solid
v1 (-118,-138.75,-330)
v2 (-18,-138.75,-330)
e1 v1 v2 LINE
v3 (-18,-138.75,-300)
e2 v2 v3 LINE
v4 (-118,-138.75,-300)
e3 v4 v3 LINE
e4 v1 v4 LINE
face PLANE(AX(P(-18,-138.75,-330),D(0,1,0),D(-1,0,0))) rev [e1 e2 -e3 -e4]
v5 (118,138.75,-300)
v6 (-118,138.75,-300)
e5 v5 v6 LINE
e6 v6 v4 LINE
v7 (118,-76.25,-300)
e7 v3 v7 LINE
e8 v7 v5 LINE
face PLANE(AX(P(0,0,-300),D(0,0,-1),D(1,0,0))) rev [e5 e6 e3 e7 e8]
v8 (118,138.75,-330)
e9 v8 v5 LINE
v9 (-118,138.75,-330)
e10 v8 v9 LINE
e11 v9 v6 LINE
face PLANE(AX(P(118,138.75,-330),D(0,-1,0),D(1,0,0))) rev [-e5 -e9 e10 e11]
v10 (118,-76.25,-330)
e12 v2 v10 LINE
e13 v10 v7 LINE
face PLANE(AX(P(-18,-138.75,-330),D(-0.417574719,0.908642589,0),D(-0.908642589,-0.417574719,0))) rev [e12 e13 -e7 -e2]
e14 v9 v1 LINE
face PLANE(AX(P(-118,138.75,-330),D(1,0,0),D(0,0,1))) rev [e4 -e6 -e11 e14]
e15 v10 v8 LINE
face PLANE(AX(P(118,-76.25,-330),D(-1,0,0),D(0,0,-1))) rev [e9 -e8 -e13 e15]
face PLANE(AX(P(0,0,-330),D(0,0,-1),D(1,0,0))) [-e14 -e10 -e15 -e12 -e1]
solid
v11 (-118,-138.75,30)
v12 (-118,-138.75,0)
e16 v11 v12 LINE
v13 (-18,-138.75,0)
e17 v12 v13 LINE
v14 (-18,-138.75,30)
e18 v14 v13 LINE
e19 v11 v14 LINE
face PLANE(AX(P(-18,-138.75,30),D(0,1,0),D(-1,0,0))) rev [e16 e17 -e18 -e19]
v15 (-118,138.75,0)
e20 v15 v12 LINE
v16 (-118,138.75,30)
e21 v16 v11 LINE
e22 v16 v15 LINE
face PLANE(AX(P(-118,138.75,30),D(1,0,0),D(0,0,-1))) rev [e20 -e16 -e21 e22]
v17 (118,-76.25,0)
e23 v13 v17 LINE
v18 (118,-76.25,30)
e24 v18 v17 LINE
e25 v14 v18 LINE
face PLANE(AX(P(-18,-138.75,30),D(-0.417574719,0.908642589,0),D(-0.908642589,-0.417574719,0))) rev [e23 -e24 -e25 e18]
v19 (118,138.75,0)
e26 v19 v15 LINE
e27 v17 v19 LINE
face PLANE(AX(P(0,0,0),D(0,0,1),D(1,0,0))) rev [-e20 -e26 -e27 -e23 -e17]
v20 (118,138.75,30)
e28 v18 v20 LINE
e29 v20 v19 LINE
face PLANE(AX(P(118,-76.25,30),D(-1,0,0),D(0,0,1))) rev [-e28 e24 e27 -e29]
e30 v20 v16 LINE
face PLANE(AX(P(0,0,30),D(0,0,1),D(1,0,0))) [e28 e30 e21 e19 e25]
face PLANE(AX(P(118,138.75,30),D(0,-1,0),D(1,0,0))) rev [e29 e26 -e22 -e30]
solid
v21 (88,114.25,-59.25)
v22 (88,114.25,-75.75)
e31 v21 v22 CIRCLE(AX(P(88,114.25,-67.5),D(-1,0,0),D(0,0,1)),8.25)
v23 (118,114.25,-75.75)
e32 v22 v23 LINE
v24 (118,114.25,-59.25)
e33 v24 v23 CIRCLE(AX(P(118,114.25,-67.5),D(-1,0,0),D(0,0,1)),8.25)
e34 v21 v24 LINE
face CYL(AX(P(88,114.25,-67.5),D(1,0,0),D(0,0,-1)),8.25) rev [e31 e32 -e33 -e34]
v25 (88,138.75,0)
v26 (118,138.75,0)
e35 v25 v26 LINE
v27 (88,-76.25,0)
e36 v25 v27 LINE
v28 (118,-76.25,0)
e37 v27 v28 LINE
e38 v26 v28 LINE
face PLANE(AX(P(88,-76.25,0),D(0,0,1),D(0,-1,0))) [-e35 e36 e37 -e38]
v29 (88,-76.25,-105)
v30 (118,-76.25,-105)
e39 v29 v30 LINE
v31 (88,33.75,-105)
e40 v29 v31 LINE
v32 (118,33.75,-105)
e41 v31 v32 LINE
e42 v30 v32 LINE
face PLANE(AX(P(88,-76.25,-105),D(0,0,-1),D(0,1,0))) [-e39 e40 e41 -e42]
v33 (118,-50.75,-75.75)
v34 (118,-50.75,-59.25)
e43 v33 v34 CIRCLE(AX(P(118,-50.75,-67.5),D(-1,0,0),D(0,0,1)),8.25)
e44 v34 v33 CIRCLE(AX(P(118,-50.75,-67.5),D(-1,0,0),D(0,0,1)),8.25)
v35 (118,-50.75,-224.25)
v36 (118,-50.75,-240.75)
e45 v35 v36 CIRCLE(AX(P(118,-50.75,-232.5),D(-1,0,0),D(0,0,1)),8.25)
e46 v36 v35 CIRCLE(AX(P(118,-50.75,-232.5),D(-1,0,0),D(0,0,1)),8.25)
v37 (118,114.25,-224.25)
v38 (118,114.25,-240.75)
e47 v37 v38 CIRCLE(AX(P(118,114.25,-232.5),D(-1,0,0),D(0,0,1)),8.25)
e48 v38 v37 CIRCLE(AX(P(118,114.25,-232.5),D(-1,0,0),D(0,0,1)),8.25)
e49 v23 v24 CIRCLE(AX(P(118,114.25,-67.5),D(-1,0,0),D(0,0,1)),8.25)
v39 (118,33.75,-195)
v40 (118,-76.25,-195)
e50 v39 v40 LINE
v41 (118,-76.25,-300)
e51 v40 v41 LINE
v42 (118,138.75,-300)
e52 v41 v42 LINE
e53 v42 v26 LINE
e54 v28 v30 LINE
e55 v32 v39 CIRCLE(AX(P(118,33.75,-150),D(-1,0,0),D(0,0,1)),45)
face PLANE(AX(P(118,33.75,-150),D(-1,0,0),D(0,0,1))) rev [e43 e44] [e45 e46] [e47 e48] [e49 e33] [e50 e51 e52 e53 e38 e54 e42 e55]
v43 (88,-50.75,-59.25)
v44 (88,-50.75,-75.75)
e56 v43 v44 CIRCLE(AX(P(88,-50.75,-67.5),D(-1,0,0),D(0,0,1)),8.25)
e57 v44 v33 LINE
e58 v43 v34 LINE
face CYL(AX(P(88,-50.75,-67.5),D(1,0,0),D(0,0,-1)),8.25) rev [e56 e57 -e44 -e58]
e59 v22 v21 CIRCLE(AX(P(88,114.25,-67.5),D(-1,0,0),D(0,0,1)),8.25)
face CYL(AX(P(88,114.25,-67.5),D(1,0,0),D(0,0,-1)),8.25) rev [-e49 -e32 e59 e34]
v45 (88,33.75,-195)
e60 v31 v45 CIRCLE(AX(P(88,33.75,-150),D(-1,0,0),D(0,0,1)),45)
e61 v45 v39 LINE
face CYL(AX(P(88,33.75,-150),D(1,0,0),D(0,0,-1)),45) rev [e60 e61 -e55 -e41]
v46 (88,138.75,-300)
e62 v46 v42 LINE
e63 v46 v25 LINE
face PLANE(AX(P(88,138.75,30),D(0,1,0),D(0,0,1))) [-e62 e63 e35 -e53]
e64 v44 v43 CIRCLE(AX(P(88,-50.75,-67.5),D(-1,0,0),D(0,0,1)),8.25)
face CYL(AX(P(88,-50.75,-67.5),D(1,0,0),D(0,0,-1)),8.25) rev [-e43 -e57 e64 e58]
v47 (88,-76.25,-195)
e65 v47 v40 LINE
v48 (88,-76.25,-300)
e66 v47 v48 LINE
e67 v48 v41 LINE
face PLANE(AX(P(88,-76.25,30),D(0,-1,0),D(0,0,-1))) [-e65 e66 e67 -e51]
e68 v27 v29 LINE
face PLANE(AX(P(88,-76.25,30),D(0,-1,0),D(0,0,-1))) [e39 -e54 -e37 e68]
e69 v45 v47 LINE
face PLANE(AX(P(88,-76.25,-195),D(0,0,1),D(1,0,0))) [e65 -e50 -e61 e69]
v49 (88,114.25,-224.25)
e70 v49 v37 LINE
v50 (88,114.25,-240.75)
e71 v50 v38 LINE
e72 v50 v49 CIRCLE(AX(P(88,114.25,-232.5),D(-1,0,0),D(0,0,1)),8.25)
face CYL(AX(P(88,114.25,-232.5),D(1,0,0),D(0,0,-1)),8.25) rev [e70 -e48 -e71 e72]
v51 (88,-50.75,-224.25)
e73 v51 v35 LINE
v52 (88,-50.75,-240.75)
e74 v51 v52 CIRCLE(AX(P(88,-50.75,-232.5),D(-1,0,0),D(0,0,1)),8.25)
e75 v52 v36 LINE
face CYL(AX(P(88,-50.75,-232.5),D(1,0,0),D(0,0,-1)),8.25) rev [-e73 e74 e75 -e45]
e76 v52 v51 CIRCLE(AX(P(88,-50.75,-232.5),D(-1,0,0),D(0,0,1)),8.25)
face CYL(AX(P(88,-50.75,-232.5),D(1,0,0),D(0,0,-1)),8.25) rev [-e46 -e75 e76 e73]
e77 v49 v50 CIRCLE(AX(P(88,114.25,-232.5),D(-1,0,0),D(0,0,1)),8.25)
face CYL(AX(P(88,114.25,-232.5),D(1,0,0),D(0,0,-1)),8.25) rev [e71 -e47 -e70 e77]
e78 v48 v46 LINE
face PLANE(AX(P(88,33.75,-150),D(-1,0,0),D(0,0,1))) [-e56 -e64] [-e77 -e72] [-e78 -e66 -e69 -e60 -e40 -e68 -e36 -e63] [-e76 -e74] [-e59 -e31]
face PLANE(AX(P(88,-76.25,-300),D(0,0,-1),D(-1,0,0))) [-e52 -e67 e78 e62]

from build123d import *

# Parameters (mm, degrees)
BOSS_EXTRUDE1_DEPTH = 30
BOSS_EXTRUDE2_START = 118
SKETCH5_R           = 8.25
BOSS_EXTRUDE2_DEPTH = 30


with BuildPart() as part:
    # Sketch1 → Boss-Extrude1 (new body)
    with BuildSketch(Plane.XY):
        Polygon((-118, 138.75), (-118, -138.75), (-18, -138.75), (118, -76.25), (118, 138.75), align=None)
    extrude(amount=BOSS_EXTRUDE1_DEPTH)


with BuildPart() as body_2:
    # Mirror2: mirrored copy
    add(part.part.mirror(Plane(origin=(0, 0, -150), x_dir=(1, 0, 0), z_dir=(0, 0, -1))))


with BuildPart() as body_3:
    # Sketch5 → Boss-Extrude2 (new body)
    with BuildSketch(Plane(origin=(0, 0, 0), x_dir=(0, 0, -1), z_dir=(1, 0, 0)).offset(BOSS_EXTRUDE2_START)):
        with BuildLine():
            Line((195, 33.75), (195, -76.25))
            Line((195, -76.25), (300, -76.25))
            Line((300, -76.25), (300, 138.75))
            Line((300, 138.75), (150, 138.75))
            Line((150, 138.75), (0, 138.75))
            Line((0, 138.75), (0, -76.25))
            Line((0, -76.25), (105, -76.25))
            Line((105, -76.25), (105, 33.75))
            ThreePointArc((105, 33.75), (150, 78.75), (195, 33.75))
        make_face()
        with Locations(Location((67.5, 114.25, 0), (0, 0, 180))):
            Circle(SKETCH5_R, mode=Mode.SUBTRACT)
        with Locations(Location((232.5, 114.25, 0), (0, 0, 180))):
            Circle(SKETCH5_R, mode=Mode.SUBTRACT)
        with Locations(Location((232.5, -50.75, 0), (0, 0, 180))):
            Circle(SKETCH5_R, mode=Mode.SUBTRACT)
        with Locations(Location((67.5, -50.75, 0), (0, 0, 180))):
            Circle(SKETCH5_R, mode=Mode.SUBTRACT)
    extrude(amount=-BOSS_EXTRUDE2_DEPTH)


solid = Compound([part.part, body_2.part, body_3.part])
